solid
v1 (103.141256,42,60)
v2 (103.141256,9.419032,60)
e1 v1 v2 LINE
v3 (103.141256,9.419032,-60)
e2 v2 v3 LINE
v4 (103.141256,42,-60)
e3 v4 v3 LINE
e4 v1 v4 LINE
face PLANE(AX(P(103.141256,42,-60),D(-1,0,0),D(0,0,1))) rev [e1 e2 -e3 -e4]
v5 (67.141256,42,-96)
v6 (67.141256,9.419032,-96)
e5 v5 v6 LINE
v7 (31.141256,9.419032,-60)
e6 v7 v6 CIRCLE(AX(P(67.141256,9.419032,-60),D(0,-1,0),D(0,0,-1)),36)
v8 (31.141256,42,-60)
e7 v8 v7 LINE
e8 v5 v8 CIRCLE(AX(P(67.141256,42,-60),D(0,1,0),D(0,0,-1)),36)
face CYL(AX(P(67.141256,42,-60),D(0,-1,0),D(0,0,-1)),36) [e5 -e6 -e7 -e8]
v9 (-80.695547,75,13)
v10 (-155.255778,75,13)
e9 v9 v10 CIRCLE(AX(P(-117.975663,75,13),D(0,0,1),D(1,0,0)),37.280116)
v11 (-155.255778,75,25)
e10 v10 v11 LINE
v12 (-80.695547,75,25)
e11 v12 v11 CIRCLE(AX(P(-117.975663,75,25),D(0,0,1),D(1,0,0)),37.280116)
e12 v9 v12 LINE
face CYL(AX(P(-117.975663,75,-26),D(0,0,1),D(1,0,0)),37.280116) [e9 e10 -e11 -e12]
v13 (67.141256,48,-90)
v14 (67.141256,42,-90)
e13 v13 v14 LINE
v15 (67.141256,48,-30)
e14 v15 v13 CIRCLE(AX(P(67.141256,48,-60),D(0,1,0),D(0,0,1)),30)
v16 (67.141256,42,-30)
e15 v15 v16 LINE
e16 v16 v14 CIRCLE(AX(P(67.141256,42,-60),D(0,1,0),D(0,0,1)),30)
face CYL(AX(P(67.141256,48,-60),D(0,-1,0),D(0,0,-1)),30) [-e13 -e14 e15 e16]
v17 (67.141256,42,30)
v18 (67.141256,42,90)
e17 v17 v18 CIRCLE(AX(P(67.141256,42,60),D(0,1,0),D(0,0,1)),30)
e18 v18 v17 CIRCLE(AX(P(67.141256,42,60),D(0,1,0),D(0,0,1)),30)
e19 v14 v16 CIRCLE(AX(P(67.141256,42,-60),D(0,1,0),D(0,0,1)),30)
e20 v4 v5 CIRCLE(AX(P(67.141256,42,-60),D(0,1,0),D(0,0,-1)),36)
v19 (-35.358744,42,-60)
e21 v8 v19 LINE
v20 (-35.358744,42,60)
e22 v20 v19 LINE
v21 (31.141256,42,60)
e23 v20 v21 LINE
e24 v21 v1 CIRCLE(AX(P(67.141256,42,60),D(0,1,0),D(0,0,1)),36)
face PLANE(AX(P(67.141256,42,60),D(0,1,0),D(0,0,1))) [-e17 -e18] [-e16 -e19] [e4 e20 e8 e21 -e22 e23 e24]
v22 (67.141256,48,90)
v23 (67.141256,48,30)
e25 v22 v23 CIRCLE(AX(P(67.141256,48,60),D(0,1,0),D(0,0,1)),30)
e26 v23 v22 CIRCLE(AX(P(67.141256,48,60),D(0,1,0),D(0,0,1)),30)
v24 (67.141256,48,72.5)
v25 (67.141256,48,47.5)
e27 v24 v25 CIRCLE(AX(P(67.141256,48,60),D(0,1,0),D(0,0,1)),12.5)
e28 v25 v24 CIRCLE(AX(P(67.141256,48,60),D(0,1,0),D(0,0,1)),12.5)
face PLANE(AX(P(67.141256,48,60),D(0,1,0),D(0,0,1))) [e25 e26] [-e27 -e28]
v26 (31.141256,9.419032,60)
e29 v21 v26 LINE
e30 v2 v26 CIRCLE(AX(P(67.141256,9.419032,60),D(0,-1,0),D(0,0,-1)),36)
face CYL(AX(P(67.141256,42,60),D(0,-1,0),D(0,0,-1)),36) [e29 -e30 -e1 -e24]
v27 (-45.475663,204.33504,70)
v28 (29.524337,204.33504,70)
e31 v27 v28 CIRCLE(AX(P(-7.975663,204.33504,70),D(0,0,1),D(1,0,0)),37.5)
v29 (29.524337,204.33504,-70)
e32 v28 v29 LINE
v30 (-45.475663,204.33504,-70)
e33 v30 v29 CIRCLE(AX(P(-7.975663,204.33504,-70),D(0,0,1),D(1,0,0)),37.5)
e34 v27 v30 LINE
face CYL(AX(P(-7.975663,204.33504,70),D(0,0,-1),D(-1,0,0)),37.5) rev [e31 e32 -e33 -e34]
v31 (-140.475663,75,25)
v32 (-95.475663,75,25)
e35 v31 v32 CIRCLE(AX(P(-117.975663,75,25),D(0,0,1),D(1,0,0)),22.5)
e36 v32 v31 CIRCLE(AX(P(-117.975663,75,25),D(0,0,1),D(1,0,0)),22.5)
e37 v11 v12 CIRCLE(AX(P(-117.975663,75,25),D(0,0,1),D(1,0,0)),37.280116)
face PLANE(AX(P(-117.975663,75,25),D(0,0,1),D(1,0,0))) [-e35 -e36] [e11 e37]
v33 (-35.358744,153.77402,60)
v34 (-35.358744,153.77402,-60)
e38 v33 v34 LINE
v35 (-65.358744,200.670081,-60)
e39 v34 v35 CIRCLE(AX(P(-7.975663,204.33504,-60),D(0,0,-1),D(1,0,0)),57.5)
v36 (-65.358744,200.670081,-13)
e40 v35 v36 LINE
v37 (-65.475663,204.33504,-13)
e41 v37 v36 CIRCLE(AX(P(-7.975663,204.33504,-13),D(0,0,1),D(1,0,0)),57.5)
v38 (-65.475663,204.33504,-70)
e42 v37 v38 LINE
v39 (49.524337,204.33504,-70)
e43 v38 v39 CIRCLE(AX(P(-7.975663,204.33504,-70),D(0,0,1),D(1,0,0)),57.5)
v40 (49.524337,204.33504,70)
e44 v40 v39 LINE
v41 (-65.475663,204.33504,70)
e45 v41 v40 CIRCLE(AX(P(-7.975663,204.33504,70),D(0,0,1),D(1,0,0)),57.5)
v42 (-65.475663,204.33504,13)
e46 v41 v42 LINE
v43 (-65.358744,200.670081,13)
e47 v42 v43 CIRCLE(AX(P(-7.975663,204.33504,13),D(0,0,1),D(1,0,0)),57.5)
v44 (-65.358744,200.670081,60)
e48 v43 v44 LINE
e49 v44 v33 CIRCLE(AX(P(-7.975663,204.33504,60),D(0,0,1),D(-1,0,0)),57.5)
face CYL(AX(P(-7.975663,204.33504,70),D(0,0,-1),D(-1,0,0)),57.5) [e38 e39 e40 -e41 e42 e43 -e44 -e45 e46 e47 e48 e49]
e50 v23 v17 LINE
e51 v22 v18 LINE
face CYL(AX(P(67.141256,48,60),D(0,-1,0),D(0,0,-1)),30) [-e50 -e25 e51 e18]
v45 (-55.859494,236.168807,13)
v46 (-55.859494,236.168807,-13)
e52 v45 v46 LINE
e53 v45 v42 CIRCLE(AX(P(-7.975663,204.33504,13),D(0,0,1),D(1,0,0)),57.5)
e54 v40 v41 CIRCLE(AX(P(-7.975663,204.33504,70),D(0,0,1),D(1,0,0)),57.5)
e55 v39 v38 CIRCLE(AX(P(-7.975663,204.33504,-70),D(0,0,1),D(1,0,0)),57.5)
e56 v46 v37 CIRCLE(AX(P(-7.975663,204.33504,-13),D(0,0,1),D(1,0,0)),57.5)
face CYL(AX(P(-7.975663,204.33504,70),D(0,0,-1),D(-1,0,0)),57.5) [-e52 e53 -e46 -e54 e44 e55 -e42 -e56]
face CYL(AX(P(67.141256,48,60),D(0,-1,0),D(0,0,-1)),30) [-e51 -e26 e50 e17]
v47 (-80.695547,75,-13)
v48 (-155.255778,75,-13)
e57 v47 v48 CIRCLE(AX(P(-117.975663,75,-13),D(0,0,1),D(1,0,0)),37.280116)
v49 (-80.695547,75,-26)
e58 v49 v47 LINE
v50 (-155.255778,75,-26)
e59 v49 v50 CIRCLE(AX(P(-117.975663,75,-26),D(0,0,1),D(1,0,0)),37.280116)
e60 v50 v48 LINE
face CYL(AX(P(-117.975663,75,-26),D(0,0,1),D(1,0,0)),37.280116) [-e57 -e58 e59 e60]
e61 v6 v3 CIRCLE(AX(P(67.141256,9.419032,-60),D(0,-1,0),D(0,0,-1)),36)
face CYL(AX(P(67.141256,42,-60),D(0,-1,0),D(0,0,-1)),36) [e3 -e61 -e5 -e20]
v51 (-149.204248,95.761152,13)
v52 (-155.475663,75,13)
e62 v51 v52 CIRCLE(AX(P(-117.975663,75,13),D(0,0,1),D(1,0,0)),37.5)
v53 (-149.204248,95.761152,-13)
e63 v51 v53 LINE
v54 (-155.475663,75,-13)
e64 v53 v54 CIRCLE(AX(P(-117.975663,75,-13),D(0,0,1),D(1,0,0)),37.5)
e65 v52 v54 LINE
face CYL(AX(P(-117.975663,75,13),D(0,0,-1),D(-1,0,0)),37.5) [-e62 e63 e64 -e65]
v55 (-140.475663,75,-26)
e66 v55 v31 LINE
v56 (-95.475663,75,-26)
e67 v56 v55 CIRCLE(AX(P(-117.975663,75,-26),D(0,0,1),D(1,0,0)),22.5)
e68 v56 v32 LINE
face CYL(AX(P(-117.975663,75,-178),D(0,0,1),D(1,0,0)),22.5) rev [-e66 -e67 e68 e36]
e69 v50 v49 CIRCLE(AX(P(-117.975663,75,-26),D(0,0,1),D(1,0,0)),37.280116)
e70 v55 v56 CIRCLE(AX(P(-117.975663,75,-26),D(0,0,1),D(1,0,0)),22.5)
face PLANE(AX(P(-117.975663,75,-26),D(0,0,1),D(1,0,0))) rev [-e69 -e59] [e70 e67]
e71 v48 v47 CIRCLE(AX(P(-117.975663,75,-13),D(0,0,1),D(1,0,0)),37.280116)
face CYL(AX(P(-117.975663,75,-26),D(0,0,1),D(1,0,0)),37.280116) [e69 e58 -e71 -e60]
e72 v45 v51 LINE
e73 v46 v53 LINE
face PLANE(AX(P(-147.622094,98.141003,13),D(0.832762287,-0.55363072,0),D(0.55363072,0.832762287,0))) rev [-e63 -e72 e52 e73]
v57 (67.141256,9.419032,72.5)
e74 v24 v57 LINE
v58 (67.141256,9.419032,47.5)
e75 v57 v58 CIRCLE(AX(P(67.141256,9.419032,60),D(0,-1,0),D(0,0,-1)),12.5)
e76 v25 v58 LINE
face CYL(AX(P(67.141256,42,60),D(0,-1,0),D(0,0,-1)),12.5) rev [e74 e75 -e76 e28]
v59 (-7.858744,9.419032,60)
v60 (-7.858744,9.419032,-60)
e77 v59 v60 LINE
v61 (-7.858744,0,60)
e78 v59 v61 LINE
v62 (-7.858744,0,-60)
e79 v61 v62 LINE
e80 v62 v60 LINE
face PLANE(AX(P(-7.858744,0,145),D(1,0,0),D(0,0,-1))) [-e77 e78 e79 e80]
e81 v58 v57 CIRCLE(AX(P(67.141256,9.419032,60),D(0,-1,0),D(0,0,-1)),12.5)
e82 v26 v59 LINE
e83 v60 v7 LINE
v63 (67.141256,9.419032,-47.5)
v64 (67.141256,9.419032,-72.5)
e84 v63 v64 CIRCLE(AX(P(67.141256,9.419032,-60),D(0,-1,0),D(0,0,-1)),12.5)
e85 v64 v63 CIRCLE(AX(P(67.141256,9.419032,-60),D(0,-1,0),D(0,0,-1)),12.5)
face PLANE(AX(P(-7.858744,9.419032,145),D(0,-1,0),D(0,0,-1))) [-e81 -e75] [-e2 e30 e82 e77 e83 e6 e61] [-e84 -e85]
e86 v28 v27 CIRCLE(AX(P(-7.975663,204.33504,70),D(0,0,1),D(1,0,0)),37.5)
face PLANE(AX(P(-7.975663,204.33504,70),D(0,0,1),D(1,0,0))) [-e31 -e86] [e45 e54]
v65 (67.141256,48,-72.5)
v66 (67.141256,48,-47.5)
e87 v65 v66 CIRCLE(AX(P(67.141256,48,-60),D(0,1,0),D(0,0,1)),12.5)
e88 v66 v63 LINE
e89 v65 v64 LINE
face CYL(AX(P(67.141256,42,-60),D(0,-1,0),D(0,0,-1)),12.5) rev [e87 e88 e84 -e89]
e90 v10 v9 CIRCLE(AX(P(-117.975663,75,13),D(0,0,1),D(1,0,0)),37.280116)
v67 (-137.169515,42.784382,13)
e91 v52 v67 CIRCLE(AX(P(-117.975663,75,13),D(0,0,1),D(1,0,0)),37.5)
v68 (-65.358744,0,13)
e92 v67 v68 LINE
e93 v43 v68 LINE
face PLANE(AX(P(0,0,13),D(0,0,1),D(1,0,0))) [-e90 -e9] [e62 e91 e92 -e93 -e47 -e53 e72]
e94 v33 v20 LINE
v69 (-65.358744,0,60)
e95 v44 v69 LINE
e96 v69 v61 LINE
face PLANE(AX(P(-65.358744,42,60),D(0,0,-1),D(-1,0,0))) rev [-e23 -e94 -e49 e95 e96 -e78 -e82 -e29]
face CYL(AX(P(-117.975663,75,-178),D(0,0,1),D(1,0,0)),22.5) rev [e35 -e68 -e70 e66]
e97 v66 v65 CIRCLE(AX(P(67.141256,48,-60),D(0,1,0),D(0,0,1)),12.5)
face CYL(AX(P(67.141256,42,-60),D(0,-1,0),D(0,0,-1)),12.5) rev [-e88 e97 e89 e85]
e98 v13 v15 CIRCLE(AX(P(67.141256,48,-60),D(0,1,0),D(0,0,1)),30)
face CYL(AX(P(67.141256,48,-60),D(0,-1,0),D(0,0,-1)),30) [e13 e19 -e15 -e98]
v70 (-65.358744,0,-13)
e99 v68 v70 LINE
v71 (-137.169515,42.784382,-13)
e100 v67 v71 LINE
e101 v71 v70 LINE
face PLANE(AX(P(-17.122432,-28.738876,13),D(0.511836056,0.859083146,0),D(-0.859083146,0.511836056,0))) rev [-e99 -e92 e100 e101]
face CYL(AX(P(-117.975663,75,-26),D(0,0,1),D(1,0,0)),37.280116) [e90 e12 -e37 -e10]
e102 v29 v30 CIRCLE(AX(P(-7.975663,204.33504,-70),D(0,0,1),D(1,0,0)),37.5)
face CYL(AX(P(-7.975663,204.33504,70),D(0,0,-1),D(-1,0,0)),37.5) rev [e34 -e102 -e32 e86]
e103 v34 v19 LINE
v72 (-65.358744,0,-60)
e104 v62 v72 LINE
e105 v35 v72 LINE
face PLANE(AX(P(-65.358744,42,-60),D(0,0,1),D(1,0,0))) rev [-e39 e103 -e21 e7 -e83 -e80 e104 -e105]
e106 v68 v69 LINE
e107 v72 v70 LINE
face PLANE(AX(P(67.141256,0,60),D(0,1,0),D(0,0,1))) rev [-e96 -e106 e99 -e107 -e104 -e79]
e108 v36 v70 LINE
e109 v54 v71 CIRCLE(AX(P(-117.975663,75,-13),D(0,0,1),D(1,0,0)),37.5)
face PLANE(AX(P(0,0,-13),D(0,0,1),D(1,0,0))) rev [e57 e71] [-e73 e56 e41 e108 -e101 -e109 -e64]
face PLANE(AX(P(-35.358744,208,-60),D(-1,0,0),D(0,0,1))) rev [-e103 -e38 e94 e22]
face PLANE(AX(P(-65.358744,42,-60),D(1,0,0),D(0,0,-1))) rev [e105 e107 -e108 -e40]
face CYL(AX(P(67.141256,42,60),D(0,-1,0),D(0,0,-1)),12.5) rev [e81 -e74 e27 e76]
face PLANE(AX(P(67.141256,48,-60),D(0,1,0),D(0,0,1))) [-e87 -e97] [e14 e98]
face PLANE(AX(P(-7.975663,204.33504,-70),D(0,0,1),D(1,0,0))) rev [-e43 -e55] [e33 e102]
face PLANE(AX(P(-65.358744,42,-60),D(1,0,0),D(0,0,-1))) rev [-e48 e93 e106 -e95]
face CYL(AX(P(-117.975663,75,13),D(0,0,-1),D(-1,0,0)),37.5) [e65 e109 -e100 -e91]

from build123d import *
from build123d.topology import SkipClean

# Parameters (mm, degrees)
BASE_PLATE_PROFILE_R       = 12.5
BASE_PLATE_DEPTH           = 42
UPRIGHT_PROFILE_W          = 30
UPRIGHT_PROFILE_H          = 120
UPRIGHT_WEB_DEPTH          = 166
UPPER_BLOCK_DEPTH          = 10
UPPER_BLOCK_DEPTH_BACK     = 130
UPPER_BLOCK_PROFILE_R      = 57.5
UPPER_BLOCK_PROFILE_R_2    = 37.5
UPPER_BLOCK_TRIM_CUT_DEPTH = 130
HOUSING_PROFILE_R          = 37.5
HOUSING_PROFILE_R_2        = 22.5
HOUSING_DEPTH              = 13
SIDE_BOSS_DEPTH            = 12
SIDE_BOSS_DEPTH_BACK       = 39
SIDE_BOSS_PROFILE_R        = 37.280115622
BORE_45_PROFILE_R          = 22.5
BORE_45_DEPTH              = 203
MOUNTING_PADS_PROFILE_R    = 30
MOUNTING_PADS_PROFILE_R_2  = 12.5
MOUNTING_PADS_DEPTH        = 6
MOUNTING_HOLES_DEPTH       = 85
MOUNTING_HOLES_DEPTH_BACK  = 317
MOUNTING_HOLES_PROFILE_W   = 111
MOUNTING_HOLES_PROFILE_H   = 9.419031608


with BuildPart() as part:
    # Base Plate Profile → Base Plate (new body)
    with BuildSketch(Plane(origin=(0, 0, 0), x_dir=(1, 0, 0), z_dir=(0, 1, 0))):
        with BuildLine():
            Line((-65.358744395, 60), (31.141255605, 60))
            ThreePointArc((31.141255605, 60), (67.141255605, 96), (103.141255605, 60))
            Line((103.141255605, 60), (103.141255605, -60))
            ThreePointArc((103.141255605, -60), (67.141255605, -96), (31.141255605, -60))
            Line((31.141255605, -60), (-65.358744395, -60))
            Line((-65.358744395, -60), (-65.358744395, 60))
        make_face()
        with Locations(Location((67.141255605, -60, 0), (0, 0, 90))):
            Circle(BASE_PLATE_PROFILE_R, mode=Mode.SUBTRACT)
        with Locations(Location((67.141255605, 60, 0), (0, 0, 90))):
            Circle(BASE_PLATE_PROFILE_R, mode=Mode.SUBTRACT)
    extrude(amount=BASE_PLATE_DEPTH)

    # Upright Profile → Upright Web (add)
    with BuildSketch(Plane(origin=(0, 42, 0), x_dir=(1, 0, 0), z_dir=(0, 1, 0))):
        with Locations((-50.358744395, 0)):
            Rectangle(UPRIGHT_PROFILE_W, UPRIGHT_PROFILE_H)
    extrude(amount=UPRIGHT_WEB_DEPTH)

    # Upper Block Profile → Upper Block (add, two sides: drawn at the far end of the back side and taken through both)
    with BuildSketch(Plane.XY.offset(60).offset(-UPPER_BLOCK_DEPTH_BACK)):
        with Locations((-7.975662641, 204.33504045)):
            Circle(UPPER_BLOCK_PROFILE_R)
        with Locations((-7.975662641, 204.33504045)):
            Circle(UPPER_BLOCK_PROFILE_R_2, mode=Mode.SUBTRACT)
    extrude(amount=UPPER_BLOCK_DEPTH + UPPER_BLOCK_DEPTH_BACK)

    # Upper Block Trim Profile → Upper Block Trim Cut (cut)
    with SkipClean():  # the faces are left unmerged after this step: merging them gives an invalid solid
        with BuildSketch(Plane.XY.offset(60)):
            with BuildLine():
                Line((-45.296140552, 208), (-35.358744395, 208))
                Line((-35.358744395, 208), (-35.358744395, 178.714407481))
                ThreePointArc((-35.358744395, 178.714407481), (-43.486916359, 192.285108524), (-45.296140552, 208))
            make_face()
        extrude(amount=-UPPER_BLOCK_TRIM_CUT_DEPTH, mode=Mode.SUBTRACT)

    # Housing Profile → Housing (add, symmetric)
    # profile 1 of 2: a face of its own
    with BuildSketch(Plane.XY):
        with BuildLine():
            ThreePointArc((-80.475662641, 75), (-99.448917842, 42.396170054), (-137.169514756, 42.784382033))
            Line((-137.169514756, 42.784382033), (-65.358744395, 0))
            Line((-65.358744395, 0), (-65.358744395, 200.670080899))
            ThreePointArc((-65.358744395, 200.670080899), (-63.521325311, 219.198733078), (-55.859494126, 236.168806836))
            Line((-55.859494126, 236.168806836), (-149.204248392, 95.761151991))
            ThreePointArc((-149.204248392, 95.761151991), (-107.131815668, 110.897924492), (-80.475662641, 75))
        make_face()
    # profile 2 of 2: a face of its own
    with BuildSketch(Plane.XY):
        with Locations((-117.975662641, 75)):
            Circle(HOUSING_PROFILE_R)
        with Locations(Location((-117.975662641, 75, 0), (0, 0, 180))):
            Circle(HOUSING_PROFILE_R_2, mode=Mode.SUBTRACT)
    extrude(amount=HOUSING_DEPTH, both=True)

    # Side Boss Profile → Side Boss (add, two sides: drawn at the far end of the back side and taken through both)
    with BuildSketch(Plane.XY.offset(13).offset(-SIDE_BOSS_DEPTH_BACK)):
        with Locations((-117.975662641, 75)):
            Circle(SIDE_BOSS_PROFILE_R)
    extrude(amount=SIDE_BOSS_DEPTH + SIDE_BOSS_DEPTH_BACK)

    # Bore Ø45 Profile → Bore Ø45 (cut)
    with BuildSketch(Plane.XY.offset(25)):
        with Locations((-117.975662641, 75)):
            Circle(BORE_45_PROFILE_R)
    extrude(amount=-BORE_45_DEPTH, mode=Mode.SUBTRACT)

    # Mounting Pads Profile → Mounting Pads (add)
    # profile 1 of 2: a face of its own
    with BuildSketch(Plane(origin=(0, 42, 0), x_dir=(1, 0, 0), z_dir=(0, 1, 0))):
        with Locations(Location((67.141255605, -60, 0), (0, 0, 270))):
            Circle(MOUNTING_PADS_PROFILE_R)
        with Locations(Location((67.141255605, -60, 0), (0, 0, 90))):
            Circle(MOUNTING_PADS_PROFILE_R_2, mode=Mode.SUBTRACT)
    # profile 2 of 2: a face of its own
    with BuildSketch(Plane(origin=(0, 42, 0), x_dir=(1, 0, 0), z_dir=(0, 1, 0))):
        with Locations(Location((67.141255605, 60, 0), (0, 0, 270))):
            Circle(MOUNTING_PADS_PROFILE_R)
        with Locations(Location((67.141255605, 60, 0), (0, 0, 90))):
            Circle(MOUNTING_PADS_PROFILE_R_2, mode=Mode.SUBTRACT)
    extrude(amount=MOUNTING_PADS_DEPTH)

    # Mounting Holes Profile → Mounting Holes (cut, two sides: drawn at the far end of the back side and taken through both)
    with BuildSketch(Plane.XY.offset(60).offset(-MOUNTING_HOLES_DEPTH_BACK)):
        with Locations((47.641255605, 4.709515804)):
            Rectangle(MOUNTING_HOLES_PROFILE_W, MOUNTING_HOLES_PROFILE_H)
    extrude(amount=MOUNTING_HOLES_DEPTH + MOUNTING_HOLES_DEPTH_BACK, mode=Mode.SUBTRACT)


solid = part.part
